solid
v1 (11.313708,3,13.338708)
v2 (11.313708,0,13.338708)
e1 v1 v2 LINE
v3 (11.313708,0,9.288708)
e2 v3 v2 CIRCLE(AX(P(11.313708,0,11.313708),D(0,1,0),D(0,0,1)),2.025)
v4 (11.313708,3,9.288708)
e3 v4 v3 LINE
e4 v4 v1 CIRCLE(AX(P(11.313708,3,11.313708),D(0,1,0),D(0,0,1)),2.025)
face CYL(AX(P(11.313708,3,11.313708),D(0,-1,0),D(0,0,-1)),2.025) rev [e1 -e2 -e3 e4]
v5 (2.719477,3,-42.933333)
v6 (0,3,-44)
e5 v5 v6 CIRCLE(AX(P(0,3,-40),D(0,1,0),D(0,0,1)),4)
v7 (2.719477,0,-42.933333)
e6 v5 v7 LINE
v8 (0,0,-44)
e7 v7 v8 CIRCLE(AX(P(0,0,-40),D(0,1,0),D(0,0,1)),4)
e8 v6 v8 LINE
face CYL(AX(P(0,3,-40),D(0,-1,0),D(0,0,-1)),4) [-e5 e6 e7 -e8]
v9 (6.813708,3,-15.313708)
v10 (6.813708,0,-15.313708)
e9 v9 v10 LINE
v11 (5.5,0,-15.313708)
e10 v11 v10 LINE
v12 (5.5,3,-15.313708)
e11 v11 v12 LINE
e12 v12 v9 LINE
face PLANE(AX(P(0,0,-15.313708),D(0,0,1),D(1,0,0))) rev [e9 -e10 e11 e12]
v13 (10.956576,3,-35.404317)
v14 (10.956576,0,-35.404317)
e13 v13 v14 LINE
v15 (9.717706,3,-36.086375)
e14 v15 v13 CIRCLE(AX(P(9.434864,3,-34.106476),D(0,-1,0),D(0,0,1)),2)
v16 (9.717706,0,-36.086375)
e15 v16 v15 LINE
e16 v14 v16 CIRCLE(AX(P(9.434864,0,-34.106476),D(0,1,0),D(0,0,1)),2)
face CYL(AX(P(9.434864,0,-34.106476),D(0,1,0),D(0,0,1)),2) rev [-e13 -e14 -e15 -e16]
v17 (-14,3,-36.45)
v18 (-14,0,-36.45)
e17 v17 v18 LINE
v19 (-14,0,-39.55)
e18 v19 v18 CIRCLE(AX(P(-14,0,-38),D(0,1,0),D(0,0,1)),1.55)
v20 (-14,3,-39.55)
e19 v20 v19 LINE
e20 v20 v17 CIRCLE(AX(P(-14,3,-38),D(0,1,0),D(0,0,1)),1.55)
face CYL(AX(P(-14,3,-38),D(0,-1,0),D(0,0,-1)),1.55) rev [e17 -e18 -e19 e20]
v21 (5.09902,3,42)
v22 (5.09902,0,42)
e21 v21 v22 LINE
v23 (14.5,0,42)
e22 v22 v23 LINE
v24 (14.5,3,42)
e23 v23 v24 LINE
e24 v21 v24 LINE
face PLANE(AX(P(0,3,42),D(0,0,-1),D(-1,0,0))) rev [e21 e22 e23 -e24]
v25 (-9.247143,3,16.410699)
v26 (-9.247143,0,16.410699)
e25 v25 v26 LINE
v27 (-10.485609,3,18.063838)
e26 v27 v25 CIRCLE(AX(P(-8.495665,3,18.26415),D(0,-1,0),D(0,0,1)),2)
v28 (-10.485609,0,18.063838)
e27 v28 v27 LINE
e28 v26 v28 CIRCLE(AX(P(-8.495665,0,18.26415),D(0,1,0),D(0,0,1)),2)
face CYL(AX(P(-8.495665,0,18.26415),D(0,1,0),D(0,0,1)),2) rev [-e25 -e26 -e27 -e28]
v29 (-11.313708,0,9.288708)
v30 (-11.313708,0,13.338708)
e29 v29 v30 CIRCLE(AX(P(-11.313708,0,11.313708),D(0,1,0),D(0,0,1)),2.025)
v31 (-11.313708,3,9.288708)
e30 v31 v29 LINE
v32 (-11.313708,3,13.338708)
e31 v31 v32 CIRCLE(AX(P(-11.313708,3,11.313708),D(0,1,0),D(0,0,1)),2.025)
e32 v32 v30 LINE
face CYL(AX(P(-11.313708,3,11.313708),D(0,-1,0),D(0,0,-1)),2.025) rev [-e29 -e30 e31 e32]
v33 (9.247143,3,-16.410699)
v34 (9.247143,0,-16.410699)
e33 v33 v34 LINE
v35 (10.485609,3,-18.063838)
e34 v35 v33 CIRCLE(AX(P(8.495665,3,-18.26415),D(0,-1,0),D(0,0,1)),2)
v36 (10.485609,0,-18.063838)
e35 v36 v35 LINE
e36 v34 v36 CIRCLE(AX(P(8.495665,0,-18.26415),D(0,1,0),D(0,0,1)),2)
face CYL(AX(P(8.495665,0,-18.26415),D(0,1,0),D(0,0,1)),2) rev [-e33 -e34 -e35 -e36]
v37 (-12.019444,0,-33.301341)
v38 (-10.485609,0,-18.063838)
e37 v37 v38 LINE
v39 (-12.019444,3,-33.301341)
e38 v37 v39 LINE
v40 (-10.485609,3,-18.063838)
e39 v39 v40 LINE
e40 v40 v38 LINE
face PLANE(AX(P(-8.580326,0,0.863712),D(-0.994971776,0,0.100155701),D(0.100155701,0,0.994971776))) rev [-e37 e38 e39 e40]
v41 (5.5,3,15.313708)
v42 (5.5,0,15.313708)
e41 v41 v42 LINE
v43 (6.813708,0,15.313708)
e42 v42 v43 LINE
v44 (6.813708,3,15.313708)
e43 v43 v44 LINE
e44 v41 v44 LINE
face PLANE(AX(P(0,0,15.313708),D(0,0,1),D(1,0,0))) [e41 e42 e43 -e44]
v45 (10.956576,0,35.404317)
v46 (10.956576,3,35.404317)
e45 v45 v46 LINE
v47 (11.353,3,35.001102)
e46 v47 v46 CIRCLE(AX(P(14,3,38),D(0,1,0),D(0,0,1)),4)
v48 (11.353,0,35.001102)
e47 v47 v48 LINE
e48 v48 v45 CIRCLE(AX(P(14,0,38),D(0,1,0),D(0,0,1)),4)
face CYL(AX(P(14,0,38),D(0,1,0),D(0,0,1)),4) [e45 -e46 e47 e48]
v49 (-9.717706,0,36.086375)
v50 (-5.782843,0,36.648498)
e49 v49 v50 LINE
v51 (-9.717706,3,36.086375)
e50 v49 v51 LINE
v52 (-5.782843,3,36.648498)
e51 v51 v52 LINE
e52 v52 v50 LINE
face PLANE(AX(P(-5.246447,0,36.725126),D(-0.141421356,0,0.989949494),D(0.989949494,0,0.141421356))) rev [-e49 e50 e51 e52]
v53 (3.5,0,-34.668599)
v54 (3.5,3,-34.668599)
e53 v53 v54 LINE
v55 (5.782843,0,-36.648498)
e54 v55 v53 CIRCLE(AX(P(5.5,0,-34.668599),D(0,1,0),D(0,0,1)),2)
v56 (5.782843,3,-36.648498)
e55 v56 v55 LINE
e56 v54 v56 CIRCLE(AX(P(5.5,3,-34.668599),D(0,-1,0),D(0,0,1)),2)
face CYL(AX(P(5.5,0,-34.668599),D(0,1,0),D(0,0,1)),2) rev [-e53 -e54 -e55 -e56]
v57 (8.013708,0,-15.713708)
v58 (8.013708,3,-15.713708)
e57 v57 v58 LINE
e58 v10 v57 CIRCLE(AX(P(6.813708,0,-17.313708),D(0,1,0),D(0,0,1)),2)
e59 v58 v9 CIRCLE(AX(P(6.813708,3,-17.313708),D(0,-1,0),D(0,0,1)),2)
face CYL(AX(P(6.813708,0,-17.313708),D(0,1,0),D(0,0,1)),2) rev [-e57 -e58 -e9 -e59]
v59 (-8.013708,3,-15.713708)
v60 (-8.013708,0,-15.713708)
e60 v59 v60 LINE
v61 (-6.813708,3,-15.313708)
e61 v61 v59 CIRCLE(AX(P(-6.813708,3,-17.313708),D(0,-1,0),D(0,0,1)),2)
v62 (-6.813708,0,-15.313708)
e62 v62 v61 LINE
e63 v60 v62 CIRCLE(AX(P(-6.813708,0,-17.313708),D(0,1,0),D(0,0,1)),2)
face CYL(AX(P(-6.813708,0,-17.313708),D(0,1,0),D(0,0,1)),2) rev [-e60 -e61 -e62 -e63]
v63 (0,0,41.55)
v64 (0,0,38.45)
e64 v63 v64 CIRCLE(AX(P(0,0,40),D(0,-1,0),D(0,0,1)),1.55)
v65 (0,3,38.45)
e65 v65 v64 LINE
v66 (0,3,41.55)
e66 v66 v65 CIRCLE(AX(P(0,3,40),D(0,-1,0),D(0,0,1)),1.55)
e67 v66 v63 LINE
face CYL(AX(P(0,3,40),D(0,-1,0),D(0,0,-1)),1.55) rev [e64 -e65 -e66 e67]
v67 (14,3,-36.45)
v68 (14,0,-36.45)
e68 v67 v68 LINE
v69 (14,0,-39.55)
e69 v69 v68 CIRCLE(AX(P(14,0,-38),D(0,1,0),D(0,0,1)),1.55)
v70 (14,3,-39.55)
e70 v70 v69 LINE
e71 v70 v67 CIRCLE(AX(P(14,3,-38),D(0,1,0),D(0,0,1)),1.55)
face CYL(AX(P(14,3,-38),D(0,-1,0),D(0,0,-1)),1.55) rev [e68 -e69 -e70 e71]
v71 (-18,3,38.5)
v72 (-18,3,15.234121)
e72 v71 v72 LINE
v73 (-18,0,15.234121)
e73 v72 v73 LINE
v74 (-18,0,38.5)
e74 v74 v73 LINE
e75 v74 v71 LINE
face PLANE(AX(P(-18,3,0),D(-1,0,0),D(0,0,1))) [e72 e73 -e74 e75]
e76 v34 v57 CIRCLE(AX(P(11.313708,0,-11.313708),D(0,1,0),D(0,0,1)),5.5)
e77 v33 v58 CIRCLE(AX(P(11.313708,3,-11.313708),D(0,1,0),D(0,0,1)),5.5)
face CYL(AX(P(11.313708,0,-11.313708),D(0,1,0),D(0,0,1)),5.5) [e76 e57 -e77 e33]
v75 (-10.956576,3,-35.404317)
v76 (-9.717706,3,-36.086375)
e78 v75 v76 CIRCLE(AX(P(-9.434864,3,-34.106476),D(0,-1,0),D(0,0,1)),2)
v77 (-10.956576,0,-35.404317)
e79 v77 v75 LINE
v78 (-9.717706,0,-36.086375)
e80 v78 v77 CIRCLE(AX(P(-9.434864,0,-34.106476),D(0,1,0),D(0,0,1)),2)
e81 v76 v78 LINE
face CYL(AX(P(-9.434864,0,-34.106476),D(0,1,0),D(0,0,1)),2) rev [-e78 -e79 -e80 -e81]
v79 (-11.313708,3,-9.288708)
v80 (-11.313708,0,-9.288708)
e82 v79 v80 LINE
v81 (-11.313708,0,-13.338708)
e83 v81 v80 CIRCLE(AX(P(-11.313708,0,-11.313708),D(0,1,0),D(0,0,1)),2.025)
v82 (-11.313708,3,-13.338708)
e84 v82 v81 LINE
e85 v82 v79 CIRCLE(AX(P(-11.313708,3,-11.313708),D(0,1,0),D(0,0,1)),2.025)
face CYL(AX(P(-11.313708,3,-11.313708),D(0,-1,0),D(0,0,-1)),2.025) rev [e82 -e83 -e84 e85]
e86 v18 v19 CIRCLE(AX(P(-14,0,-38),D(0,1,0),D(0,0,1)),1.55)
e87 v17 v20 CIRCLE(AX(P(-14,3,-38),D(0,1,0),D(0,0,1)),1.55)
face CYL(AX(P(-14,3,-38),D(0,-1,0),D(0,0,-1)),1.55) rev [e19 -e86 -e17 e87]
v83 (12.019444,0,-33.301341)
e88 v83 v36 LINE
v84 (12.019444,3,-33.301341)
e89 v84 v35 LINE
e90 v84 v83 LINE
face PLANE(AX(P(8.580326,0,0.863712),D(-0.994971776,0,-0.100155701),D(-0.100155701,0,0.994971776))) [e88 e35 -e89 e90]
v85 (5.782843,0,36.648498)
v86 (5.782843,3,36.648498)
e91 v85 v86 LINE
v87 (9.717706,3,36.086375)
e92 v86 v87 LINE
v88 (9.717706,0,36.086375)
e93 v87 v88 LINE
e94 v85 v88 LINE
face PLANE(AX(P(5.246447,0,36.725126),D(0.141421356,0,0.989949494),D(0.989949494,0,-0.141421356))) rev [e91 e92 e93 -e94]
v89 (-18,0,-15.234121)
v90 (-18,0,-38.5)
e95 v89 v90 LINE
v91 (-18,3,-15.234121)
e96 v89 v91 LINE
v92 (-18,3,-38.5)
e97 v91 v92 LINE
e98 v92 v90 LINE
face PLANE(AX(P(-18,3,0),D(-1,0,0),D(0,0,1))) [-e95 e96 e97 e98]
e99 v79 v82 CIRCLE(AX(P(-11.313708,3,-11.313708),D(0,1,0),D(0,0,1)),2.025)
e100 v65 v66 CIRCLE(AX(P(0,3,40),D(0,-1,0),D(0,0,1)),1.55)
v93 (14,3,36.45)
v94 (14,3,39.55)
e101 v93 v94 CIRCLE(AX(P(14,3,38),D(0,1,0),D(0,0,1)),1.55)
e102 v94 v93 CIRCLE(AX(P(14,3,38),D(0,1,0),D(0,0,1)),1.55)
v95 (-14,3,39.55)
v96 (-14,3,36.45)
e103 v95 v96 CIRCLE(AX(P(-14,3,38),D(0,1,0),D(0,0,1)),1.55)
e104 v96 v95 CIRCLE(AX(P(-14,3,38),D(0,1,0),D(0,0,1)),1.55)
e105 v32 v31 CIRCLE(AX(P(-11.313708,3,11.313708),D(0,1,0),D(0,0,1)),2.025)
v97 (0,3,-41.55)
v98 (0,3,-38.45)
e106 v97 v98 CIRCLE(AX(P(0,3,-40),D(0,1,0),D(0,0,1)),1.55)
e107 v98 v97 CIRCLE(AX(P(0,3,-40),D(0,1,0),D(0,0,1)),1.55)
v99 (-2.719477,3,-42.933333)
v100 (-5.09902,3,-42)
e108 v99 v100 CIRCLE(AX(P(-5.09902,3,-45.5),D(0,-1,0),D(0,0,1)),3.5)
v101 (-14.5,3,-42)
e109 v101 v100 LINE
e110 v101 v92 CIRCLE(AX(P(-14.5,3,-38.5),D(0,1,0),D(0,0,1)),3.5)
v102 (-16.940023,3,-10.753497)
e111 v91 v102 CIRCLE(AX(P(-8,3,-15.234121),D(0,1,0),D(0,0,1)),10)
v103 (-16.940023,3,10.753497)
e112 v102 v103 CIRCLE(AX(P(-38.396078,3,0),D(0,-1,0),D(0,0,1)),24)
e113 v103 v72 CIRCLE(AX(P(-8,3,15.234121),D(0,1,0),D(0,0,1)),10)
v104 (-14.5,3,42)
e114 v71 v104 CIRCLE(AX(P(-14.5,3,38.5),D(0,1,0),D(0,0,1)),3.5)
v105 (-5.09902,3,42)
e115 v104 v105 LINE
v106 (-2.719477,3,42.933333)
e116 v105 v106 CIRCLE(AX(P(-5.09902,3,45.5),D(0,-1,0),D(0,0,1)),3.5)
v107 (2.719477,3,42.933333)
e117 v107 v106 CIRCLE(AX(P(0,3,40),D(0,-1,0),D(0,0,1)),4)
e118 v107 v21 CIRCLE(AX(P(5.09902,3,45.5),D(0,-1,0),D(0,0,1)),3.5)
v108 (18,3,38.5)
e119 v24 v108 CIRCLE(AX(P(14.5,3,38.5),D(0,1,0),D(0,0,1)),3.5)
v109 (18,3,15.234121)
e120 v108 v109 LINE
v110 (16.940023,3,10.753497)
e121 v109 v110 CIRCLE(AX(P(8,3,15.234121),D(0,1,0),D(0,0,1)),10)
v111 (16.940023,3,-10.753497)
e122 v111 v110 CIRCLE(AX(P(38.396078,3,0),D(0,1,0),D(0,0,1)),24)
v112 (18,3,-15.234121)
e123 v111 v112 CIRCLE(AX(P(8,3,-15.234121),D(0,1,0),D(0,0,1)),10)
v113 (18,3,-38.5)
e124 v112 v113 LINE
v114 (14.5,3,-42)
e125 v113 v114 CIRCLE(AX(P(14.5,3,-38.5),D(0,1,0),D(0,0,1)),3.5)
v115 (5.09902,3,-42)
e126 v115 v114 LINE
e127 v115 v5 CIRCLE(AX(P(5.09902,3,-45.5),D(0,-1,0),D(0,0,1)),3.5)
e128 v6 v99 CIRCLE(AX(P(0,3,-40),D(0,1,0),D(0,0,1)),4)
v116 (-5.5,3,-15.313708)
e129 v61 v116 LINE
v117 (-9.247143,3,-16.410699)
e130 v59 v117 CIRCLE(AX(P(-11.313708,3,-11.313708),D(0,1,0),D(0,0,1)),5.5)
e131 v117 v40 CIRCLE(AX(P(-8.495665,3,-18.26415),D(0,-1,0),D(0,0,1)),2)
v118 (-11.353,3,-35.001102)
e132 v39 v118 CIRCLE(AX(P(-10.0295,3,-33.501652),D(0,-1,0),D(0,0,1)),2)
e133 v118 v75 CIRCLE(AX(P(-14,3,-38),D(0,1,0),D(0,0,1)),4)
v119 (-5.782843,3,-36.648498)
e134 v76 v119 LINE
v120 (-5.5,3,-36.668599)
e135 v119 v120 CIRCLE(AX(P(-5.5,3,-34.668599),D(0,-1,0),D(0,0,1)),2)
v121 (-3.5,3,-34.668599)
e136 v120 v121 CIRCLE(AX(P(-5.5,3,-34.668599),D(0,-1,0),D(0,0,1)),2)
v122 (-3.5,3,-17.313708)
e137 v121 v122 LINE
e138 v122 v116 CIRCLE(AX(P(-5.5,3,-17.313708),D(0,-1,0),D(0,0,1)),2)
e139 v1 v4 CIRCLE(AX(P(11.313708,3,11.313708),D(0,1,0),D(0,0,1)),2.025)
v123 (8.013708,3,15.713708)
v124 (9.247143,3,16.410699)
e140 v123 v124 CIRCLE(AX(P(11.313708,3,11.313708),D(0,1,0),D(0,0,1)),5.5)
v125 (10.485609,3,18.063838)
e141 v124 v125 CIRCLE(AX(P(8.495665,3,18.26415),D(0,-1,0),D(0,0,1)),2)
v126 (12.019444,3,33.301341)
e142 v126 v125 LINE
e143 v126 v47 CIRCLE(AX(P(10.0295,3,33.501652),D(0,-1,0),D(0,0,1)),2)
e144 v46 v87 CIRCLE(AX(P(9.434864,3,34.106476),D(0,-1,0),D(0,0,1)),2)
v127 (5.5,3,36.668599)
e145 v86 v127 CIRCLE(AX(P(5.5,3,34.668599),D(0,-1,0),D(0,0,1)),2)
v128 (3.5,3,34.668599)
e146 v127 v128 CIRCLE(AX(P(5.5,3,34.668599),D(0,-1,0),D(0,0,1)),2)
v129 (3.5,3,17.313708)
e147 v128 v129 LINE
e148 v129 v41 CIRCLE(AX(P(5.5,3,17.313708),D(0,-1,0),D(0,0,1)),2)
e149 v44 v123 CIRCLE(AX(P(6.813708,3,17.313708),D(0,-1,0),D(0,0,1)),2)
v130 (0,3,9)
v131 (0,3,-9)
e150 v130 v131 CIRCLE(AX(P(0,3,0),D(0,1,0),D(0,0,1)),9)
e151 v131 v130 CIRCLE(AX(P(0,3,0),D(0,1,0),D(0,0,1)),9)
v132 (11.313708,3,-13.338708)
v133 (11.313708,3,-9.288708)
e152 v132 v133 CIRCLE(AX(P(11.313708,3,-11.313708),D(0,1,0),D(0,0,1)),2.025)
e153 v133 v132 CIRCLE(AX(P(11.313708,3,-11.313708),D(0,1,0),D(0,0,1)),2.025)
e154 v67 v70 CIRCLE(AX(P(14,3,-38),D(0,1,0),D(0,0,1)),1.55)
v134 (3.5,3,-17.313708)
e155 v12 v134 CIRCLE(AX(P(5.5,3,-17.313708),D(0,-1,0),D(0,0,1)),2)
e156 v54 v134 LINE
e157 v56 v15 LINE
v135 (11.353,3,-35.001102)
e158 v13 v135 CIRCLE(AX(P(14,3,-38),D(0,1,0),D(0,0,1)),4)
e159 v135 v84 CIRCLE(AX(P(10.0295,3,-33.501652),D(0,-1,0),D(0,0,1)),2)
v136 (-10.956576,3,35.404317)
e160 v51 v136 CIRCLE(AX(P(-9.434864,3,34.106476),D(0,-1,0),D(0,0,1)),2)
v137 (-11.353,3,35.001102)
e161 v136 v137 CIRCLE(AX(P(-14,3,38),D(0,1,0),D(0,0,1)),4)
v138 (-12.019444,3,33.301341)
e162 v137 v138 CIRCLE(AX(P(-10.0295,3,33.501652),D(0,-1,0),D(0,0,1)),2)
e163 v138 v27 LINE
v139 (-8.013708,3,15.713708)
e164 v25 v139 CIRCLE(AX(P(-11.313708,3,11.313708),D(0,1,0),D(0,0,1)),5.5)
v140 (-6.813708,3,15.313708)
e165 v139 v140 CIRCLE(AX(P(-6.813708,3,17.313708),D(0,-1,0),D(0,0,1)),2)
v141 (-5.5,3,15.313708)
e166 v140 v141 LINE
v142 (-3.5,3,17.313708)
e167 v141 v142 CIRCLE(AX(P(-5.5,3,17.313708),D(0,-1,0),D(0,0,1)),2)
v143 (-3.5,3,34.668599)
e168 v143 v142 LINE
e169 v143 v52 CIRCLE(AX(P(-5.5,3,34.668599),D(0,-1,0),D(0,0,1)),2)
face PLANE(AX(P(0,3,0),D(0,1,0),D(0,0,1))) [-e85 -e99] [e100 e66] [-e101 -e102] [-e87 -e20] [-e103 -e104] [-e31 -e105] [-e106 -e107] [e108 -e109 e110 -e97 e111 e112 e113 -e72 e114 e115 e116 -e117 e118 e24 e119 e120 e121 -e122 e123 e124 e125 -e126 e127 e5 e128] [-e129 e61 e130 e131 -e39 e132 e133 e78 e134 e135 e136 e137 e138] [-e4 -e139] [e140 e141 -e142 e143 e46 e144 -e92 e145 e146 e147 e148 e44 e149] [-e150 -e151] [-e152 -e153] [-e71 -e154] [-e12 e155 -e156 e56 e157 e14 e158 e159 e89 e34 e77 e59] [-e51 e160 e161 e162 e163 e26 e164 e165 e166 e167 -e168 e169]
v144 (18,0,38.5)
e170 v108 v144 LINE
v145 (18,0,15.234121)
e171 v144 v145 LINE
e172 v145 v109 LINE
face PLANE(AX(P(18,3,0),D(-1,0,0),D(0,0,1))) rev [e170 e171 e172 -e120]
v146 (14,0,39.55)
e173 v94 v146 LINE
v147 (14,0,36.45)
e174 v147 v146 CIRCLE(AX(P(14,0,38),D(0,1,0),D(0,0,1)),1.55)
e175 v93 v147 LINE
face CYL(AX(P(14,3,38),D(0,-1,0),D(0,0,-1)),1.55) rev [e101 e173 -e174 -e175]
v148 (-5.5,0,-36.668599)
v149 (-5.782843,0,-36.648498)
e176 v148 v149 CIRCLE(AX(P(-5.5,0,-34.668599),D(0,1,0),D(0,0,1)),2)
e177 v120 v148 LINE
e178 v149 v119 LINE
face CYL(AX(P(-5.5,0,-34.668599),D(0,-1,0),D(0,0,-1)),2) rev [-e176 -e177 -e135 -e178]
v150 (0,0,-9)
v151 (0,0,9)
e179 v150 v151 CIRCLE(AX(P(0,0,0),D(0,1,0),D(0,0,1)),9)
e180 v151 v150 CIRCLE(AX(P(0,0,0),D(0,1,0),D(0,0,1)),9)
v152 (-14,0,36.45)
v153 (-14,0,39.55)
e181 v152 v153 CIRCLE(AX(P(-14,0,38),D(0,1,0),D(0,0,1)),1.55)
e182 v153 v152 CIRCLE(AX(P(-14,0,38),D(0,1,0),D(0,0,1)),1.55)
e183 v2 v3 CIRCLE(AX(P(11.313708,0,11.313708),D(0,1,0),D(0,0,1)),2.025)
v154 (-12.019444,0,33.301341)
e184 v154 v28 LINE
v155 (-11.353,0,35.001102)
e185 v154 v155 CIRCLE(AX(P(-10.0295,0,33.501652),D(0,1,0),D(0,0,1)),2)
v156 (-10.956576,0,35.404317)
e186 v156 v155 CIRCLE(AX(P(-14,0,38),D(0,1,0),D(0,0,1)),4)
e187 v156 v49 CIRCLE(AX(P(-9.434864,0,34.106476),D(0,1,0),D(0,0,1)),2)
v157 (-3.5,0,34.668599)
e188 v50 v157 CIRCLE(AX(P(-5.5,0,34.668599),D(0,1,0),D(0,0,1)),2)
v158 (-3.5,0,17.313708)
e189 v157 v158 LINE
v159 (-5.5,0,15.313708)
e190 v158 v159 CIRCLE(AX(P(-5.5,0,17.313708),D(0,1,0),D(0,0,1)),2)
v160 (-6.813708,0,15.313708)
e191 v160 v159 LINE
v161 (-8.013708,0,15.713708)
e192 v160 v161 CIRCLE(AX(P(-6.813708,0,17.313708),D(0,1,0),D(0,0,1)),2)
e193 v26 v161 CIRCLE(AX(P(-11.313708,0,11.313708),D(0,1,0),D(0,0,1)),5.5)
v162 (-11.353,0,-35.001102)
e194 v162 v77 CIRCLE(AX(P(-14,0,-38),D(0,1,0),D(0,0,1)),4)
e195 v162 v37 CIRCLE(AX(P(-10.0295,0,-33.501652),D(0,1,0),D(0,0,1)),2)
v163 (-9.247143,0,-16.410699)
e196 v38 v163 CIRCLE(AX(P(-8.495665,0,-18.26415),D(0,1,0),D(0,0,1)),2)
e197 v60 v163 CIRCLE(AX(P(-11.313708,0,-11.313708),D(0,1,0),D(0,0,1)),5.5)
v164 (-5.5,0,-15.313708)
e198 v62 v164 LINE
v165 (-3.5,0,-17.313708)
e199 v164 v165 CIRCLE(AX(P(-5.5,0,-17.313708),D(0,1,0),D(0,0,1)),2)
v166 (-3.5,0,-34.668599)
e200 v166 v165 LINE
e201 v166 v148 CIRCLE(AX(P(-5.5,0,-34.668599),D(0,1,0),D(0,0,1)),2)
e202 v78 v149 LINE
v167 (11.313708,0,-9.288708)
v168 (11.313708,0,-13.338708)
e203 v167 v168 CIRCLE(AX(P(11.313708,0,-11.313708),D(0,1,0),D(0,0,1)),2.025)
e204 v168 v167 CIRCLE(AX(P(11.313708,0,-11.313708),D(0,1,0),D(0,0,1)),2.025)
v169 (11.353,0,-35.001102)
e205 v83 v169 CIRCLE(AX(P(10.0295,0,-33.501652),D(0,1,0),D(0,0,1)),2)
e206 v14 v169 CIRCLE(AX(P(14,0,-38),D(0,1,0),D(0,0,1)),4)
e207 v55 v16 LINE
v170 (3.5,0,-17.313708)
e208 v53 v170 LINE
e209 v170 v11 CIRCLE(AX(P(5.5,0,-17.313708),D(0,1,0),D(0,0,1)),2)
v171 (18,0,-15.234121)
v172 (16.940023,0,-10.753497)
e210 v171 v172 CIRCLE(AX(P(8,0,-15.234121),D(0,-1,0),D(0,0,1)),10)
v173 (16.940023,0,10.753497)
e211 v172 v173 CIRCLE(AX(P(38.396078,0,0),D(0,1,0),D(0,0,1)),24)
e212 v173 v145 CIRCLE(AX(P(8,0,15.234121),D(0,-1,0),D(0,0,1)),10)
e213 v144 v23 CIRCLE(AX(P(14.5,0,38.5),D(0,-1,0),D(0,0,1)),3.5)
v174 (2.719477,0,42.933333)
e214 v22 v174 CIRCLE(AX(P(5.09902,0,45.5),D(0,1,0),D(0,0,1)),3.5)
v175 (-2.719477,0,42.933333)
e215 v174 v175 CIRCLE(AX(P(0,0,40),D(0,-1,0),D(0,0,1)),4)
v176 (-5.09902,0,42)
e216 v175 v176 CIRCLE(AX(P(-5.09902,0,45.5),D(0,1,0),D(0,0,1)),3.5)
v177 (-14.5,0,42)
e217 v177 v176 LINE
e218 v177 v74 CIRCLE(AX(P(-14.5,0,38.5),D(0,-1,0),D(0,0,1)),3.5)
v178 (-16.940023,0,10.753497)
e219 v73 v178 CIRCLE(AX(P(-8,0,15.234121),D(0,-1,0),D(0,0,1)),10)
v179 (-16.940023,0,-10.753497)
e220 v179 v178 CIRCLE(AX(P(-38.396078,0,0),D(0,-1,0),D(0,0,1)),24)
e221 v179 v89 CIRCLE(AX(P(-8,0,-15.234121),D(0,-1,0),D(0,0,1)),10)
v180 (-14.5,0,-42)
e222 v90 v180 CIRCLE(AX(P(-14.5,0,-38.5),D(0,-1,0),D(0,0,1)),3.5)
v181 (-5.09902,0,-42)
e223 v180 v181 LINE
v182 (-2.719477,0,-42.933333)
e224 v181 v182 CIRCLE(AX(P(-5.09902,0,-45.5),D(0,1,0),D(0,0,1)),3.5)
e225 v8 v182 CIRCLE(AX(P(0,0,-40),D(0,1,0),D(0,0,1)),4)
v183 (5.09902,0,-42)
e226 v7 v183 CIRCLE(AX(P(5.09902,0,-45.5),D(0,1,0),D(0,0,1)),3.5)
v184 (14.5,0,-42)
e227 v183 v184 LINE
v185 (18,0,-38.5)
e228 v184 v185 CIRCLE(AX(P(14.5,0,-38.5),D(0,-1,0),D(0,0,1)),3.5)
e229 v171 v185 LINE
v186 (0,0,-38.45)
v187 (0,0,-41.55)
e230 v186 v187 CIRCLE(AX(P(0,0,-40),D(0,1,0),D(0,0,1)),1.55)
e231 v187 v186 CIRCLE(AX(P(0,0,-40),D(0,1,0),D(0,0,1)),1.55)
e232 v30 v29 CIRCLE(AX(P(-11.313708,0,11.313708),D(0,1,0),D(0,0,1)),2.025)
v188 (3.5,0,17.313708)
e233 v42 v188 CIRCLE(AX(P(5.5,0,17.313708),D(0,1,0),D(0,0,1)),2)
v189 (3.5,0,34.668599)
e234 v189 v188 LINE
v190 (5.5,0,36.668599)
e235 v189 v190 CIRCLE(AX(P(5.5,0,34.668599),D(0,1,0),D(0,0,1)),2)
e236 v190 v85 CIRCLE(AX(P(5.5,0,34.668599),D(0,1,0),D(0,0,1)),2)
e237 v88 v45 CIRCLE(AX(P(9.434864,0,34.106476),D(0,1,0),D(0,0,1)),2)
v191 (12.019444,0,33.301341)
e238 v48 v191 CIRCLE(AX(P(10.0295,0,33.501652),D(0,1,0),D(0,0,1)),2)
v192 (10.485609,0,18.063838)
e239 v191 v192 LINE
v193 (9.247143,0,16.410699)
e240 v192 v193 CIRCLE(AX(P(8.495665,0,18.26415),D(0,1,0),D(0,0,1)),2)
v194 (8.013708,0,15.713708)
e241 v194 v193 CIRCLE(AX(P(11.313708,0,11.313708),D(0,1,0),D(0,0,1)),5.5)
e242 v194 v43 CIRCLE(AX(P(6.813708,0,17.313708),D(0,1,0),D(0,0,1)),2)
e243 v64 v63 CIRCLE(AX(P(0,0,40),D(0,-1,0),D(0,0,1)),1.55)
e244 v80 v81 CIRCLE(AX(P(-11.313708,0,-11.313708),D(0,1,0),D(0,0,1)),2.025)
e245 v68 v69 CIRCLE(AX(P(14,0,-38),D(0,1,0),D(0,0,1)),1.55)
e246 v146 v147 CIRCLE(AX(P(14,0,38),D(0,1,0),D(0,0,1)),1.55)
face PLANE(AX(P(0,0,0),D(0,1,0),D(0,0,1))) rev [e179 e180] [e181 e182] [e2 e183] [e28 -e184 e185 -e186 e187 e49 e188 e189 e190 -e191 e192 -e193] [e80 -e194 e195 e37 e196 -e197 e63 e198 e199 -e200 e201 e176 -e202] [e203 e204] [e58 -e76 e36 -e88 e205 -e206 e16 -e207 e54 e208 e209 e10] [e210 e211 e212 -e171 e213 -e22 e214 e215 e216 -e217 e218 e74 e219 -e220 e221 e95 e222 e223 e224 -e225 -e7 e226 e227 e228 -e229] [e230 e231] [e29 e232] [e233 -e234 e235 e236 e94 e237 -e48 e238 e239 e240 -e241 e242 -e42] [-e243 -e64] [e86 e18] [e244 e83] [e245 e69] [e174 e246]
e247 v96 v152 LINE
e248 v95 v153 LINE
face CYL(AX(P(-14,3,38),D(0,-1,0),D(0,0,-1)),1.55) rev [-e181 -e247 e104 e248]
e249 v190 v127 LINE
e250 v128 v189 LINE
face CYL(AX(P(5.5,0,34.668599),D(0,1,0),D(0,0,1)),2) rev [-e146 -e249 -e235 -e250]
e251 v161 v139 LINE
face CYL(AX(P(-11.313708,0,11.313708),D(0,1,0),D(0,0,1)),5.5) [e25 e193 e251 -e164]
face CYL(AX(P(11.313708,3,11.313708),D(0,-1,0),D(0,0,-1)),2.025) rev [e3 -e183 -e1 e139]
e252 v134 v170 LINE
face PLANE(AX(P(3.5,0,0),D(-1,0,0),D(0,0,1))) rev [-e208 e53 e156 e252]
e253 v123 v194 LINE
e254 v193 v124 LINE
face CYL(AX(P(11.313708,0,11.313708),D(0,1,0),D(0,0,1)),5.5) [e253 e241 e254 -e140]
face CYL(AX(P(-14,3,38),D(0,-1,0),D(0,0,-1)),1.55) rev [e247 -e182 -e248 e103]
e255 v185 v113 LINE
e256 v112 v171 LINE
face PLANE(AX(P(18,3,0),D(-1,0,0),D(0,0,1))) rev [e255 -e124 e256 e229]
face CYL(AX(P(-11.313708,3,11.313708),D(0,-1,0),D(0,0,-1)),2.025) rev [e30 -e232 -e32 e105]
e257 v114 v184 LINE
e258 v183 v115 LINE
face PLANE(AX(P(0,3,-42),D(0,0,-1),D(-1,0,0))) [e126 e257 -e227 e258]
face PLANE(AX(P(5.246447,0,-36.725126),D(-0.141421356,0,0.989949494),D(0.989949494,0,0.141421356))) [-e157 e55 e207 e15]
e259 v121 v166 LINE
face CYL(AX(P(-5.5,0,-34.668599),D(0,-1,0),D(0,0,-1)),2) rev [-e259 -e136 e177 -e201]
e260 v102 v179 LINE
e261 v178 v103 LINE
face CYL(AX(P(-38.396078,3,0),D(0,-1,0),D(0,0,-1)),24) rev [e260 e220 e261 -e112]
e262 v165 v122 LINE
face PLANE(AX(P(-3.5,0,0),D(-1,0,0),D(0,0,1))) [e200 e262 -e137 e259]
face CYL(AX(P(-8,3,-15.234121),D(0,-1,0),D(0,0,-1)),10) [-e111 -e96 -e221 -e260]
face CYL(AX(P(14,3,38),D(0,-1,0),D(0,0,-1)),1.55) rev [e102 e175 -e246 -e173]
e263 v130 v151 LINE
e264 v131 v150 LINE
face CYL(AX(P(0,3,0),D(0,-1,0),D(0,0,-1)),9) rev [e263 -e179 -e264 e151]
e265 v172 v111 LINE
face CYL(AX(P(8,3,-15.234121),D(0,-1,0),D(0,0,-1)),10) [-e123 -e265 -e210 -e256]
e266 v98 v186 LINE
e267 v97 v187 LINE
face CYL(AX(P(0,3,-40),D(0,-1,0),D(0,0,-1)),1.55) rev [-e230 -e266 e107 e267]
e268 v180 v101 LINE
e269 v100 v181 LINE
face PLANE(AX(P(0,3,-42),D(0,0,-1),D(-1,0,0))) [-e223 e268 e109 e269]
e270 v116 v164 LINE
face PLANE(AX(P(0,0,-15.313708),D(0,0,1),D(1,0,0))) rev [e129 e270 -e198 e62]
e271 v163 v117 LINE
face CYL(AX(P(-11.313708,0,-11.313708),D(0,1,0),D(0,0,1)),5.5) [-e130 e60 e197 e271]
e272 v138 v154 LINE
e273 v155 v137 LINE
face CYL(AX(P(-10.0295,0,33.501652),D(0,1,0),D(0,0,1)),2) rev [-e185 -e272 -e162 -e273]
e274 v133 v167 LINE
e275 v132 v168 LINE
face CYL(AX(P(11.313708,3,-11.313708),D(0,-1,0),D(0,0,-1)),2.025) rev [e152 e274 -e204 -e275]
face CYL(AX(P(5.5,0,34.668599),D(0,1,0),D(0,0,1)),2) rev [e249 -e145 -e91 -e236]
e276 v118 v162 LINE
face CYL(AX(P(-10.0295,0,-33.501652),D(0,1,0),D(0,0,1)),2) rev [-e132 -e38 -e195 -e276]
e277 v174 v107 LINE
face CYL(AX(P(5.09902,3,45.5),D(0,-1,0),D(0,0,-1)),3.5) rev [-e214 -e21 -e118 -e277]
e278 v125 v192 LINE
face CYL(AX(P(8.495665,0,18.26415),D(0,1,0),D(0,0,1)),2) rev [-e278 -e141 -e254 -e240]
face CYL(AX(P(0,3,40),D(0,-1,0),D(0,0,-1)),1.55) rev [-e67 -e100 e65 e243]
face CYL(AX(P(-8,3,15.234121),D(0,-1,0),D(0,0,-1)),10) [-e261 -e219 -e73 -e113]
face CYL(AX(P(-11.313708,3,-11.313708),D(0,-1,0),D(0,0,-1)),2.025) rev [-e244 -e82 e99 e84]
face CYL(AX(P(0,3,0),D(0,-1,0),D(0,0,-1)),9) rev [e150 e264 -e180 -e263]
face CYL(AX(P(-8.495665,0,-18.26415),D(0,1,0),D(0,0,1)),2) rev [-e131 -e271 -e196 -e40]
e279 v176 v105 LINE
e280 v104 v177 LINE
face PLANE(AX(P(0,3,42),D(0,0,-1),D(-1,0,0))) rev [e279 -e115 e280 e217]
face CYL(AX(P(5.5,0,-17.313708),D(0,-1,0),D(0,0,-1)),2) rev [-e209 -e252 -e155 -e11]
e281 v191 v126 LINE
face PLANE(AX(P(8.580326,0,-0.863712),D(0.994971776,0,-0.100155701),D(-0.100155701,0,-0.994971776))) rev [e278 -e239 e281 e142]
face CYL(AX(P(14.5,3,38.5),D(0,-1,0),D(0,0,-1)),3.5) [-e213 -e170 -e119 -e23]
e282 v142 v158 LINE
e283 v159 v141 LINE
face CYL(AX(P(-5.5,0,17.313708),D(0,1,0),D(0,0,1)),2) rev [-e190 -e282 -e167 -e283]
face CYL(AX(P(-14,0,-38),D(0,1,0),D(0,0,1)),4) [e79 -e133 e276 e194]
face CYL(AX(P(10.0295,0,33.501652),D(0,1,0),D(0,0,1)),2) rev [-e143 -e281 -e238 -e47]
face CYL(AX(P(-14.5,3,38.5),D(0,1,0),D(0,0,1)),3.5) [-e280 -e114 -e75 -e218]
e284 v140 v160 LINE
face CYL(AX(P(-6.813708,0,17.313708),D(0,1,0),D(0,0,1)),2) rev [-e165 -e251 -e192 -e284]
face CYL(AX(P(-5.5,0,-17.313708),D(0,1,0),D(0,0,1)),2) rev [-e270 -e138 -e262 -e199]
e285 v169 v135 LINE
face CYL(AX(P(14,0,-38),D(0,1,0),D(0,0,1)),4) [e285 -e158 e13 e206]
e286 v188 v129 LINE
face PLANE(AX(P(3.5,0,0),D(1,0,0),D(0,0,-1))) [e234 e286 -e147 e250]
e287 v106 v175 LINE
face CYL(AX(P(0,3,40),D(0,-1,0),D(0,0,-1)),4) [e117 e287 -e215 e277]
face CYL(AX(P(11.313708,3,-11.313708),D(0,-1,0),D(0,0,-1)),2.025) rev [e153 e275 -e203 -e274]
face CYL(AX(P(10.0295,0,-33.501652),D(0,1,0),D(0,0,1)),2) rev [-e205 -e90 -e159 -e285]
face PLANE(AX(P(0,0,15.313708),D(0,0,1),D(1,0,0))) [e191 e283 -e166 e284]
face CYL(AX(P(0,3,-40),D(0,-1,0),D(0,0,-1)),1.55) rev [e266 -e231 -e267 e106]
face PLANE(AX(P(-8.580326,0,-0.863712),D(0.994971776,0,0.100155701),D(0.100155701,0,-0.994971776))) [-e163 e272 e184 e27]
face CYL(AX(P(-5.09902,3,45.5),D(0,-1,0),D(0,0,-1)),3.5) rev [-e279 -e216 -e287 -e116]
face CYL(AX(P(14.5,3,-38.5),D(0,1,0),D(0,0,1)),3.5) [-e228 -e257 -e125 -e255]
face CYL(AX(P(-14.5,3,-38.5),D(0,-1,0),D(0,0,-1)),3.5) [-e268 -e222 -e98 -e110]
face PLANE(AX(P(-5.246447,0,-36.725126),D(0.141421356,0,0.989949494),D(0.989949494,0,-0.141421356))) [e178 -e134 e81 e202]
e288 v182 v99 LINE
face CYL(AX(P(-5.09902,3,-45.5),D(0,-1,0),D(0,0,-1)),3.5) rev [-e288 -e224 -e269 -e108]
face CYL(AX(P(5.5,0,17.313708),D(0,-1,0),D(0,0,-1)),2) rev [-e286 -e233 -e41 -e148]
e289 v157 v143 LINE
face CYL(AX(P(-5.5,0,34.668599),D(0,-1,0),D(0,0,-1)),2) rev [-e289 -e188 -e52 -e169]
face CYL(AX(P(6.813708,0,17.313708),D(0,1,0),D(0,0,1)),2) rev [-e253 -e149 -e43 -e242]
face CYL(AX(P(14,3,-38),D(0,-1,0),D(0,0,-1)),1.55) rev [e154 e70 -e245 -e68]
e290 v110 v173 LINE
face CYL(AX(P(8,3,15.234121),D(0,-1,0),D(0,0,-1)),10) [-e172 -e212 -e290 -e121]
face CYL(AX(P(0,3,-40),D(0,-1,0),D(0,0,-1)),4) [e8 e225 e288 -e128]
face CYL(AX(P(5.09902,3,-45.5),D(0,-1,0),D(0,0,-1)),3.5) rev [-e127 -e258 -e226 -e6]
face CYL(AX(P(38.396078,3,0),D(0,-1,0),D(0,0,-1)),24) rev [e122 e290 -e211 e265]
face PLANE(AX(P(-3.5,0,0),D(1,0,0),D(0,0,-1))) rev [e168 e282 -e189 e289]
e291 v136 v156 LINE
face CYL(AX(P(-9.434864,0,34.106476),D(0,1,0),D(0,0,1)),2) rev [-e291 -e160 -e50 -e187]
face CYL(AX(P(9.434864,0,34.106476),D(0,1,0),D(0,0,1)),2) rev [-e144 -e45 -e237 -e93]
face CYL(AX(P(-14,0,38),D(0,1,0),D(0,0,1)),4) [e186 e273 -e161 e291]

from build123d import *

# Parameters (mm, degrees)
SKETCH_3_R          = 1.55
SKETCH_3_R_2        = 2.025
SKETCH_3_R_3        = 9
EXTRUDE_1_DEPTH     = 3
CUT_EXTRUDE_2_DEPTH = 3
FILLET_3_R          = 2
FILLET_4_R          = 3.5
FILLET_5_R          = 10


with BuildPart() as part:
    # 草图3 → 凸台-拉伸1 (new body)
    with BuildSketch(Plane(origin=(0, 0, 0), x_dir=(1, 0, 0), z_dir=(0, 1, 0))):
        with BuildLine():
            Line((-18, -12.649110641), (-18, -42))
            Line((-18, -42), (-3.464101615, -42))
            ThreePointArc((-3.464101615, -42), (0, -44), (3.464101615, -42))
            Line((3.464101615, -42), (18, -42))
            Line((18, -42), (18, -12.649110641))
            ThreePointArc((18, -12.649110641), (14.396078054, 0), (18, 12.649110641))
            Line((18, 12.649110641), (18, 42))
            Line((18, 42), (3.464101615, 42))
            ThreePointArc((3.464101615, 42), (0, 44), (-3.464101615, 42))
            Line((-3.464101615, 42), (-18, 42))
            Line((-18, 42), (-18, 12.649110641))
            ThreePointArc((-18, 12.649110641), (-14.396078054, 0), (-18, -12.649110641))
        make_face()
        with Locations(Location((-14, -38, 0), (0, 0, 270))):
            Circle(SKETCH_3_R, mode=Mode.SUBTRACT)
        with Locations(Location((-11.313708499, -11.313708499, 0), (0, 0, 270))):
            Circle(SKETCH_3_R_2, mode=Mode.SUBTRACT)
        with Locations(Location((14, -38, 0), (0, 0, 270))):
            Circle(SKETCH_3_R, mode=Mode.SUBTRACT)
        with Locations(Location((11.313708499, -11.313708499, 0), (0, 0, 270))):
            Circle(SKETCH_3_R_2, mode=Mode.SUBTRACT)
        with Locations(Location((-11.313708499, 11.313708499, 0), (0, 0, 270))):
            Circle(SKETCH_3_R_2, mode=Mode.SUBTRACT)
        with Locations(Location((-14, 38, 0), (0, 0, 270))):
            Circle(SKETCH_3_R, mode=Mode.SUBTRACT)
        with Locations(Location((0, 0, 0), (0, 0, 270))):
            Circle(SKETCH_3_R_3, mode=Mode.SUBTRACT)
        with Locations(Location((11.313708499, 11.313708499, 0), (0, 0, 270))):
            Circle(SKETCH_3_R_2, mode=Mode.SUBTRACT)
        with Locations(Location((14, 38, 0), (0, 0, 270))):
            Circle(SKETCH_3_R, mode=Mode.SUBTRACT)
        with Locations(Location((0, -40, 0), (0, 0, 270))):
            Circle(SKETCH_3_R, mode=Mode.SUBTRACT)
        with Locations(Location((0, 40, 0), (0, 0, 270))):
            Circle(SKETCH_3_R, mode=Mode.SUBTRACT)
    extrude(amount=EXTRUDE_1_DEPTH)

    # 草图8 → 切除-拉伸2 (cut)
    with BuildSketch(Plane(origin=(0, 3, 0), x_dir=(1, 0, 0), z_dir=(0, 1, 0))):
        with BuildLine():
            Line((-3.5, 36.974618639), (-10.555330306, 35.966714309))
            ThreePointArc((-10.555330306, 35.966714309), (-11.241007094, 35.103802813), (-12.136155057, 34.46077946))
            Line((-12.136155057, 34.46077946), (-10.351224988, 16.728837813))
            ThreePointArc((-10.351224988, 16.728837813), (-8.841586099, 16.226814527), (-7.538791281, 15.313708499))
            Line((-7.538791281, 15.313708499), (-3.5, 15.313708499))
            Line((-3.5, 15.313708499), (-3.5, 36.974618639))
        make_face()
        with BuildLine():
            Line((3.5, 36.974618639), (3.5, 15.313708499))
            Line((3.5, 15.313708499), (7.538791281, 15.313708499))
            ThreePointArc((7.538791281, 15.313708499), (8.841586099, 16.226814527), (10.351224988, 16.728837813))
            Line((10.351224988, 16.728837813), (12.136155057, 34.46077946))
            ThreePointArc((12.136155057, 34.46077946), (11.241007094, 35.103802813), (10.555330306, 35.966714309))
            Line((10.555330306, 35.966714309), (3.5, 36.974618639))
        make_face()
        with BuildLine():
            Line((3.5, -36.974618639), (10.555330306, -35.966714309))
            ThreePointArc((10.555330306, -35.966714309), (11.241007094, -35.103802813), (12.136155057, -34.46077946))
            Line((12.136155057, -34.46077946), (10.351224988, -16.728837813))
            ThreePointArc((10.351224988, -16.728837813), (8.841586099, -16.226814527), (7.538791281, -15.313708499))
            Line((7.538791281, -15.313708499), (3.5, -15.313708499))
            Line((3.5, -15.313708499), (3.5, -36.974618639))
        make_face()
        with BuildLine():
            Line((-10.555330306, -35.966714309), (-3.5, -36.974618639))
            Line((-3.5, -36.974618639), (-3.5, -15.313708499))
            Line((-3.5, -15.313708499), (-7.538791281, -15.313708499))
            ThreePointArc((-7.538791281, -15.313708499), (-8.841586099, -16.226814527), (-10.351224988, -16.728837813))
            Line((-10.351224988, -16.728837813), (-12.136155057, -34.46077946))
            ThreePointArc((-12.136155057, -34.46077946), (-11.241007094, -35.103802813), (-10.555330306, -35.966714309))
        make_face()
    extrude(amount=-CUT_EXTRUDE_2_DEPTH, mode=Mode.SUBTRACT)

    # 圆角3
    fillet_3_edges = [part.edges().sort_by_distance(p)[0] for p in [
        (7.538791281, 1.5, -15.313708499),
        (3.5, 1.5, -15.313708499),
        (3.5, 1.5, -36.974618639),
        (10.555330306, 1.5, -35.966714309),
        (12.136155057, 1.5, -34.46077946),
        (-10.351224988, 1.5, 16.728837813),
        (-7.538791281, 1.5, 15.313708499),
        (-3.5, 1.5, 15.313708499),
        (-3.5, 1.5, 36.974618639),
        (-10.555330306, 1.5, 35.966714309),
        (-12.136155057, 1.5, 34.46077946),
        (7.538791281, 1.5, 15.313708499),
        (10.351224988, 1.5, 16.728837813),
        (12.136155057, 1.5, 34.46077946),
        (10.555330306, 1.5, 35.966714309),
        (3.5, 1.5, 36.974618639),
        (3.5, 1.5, 15.313708499),
        (-7.538791281, 1.5, -15.313708499),
        (-10.351224988, 1.5, -16.728837813),
        (-12.136155057, 1.5, -34.46077946),
        (-10.555330306, 1.5, -35.966714309),
        (-3.5, 1.5, -36.974618639),
        (-3.5, 1.5, -15.313708499),
        (10.351224988, 1.5, -16.728837813),
    ]]
    fillet(fillet_3_edges, radius=FILLET_3_R)

    # 圆角4
    fillet_4_edges = [part.edges().sort_by_distance(p)[0] for p in [
        (-18, 1.5, 42),
        (-18, 1.5, -42),
        (-3.464101615, 1.5, -42),
        (3.464101615, 1.5, -42),
        (18, 1.5, -42),
        (18, 1.5, 42),
        (3.464101615, 1.5, 42),
        (-3.464101615, 1.5, 42),
    ]]
    fillet(fillet_4_edges, radius=FILLET_4_R)

    # 圆角5
    fillet_5_edges = [part.edges().sort_by_distance(p)[0] for p in [
        (-18, 1.5, 12.649110641),
        (-18, 1.5, -12.649110641),
        (18, 1.5, -12.649110641),
        (18, 1.5, 12.649110641),
    ]]
    fillet(fillet_5_edges, radius=FILLET_5_R)


solid = part.part
